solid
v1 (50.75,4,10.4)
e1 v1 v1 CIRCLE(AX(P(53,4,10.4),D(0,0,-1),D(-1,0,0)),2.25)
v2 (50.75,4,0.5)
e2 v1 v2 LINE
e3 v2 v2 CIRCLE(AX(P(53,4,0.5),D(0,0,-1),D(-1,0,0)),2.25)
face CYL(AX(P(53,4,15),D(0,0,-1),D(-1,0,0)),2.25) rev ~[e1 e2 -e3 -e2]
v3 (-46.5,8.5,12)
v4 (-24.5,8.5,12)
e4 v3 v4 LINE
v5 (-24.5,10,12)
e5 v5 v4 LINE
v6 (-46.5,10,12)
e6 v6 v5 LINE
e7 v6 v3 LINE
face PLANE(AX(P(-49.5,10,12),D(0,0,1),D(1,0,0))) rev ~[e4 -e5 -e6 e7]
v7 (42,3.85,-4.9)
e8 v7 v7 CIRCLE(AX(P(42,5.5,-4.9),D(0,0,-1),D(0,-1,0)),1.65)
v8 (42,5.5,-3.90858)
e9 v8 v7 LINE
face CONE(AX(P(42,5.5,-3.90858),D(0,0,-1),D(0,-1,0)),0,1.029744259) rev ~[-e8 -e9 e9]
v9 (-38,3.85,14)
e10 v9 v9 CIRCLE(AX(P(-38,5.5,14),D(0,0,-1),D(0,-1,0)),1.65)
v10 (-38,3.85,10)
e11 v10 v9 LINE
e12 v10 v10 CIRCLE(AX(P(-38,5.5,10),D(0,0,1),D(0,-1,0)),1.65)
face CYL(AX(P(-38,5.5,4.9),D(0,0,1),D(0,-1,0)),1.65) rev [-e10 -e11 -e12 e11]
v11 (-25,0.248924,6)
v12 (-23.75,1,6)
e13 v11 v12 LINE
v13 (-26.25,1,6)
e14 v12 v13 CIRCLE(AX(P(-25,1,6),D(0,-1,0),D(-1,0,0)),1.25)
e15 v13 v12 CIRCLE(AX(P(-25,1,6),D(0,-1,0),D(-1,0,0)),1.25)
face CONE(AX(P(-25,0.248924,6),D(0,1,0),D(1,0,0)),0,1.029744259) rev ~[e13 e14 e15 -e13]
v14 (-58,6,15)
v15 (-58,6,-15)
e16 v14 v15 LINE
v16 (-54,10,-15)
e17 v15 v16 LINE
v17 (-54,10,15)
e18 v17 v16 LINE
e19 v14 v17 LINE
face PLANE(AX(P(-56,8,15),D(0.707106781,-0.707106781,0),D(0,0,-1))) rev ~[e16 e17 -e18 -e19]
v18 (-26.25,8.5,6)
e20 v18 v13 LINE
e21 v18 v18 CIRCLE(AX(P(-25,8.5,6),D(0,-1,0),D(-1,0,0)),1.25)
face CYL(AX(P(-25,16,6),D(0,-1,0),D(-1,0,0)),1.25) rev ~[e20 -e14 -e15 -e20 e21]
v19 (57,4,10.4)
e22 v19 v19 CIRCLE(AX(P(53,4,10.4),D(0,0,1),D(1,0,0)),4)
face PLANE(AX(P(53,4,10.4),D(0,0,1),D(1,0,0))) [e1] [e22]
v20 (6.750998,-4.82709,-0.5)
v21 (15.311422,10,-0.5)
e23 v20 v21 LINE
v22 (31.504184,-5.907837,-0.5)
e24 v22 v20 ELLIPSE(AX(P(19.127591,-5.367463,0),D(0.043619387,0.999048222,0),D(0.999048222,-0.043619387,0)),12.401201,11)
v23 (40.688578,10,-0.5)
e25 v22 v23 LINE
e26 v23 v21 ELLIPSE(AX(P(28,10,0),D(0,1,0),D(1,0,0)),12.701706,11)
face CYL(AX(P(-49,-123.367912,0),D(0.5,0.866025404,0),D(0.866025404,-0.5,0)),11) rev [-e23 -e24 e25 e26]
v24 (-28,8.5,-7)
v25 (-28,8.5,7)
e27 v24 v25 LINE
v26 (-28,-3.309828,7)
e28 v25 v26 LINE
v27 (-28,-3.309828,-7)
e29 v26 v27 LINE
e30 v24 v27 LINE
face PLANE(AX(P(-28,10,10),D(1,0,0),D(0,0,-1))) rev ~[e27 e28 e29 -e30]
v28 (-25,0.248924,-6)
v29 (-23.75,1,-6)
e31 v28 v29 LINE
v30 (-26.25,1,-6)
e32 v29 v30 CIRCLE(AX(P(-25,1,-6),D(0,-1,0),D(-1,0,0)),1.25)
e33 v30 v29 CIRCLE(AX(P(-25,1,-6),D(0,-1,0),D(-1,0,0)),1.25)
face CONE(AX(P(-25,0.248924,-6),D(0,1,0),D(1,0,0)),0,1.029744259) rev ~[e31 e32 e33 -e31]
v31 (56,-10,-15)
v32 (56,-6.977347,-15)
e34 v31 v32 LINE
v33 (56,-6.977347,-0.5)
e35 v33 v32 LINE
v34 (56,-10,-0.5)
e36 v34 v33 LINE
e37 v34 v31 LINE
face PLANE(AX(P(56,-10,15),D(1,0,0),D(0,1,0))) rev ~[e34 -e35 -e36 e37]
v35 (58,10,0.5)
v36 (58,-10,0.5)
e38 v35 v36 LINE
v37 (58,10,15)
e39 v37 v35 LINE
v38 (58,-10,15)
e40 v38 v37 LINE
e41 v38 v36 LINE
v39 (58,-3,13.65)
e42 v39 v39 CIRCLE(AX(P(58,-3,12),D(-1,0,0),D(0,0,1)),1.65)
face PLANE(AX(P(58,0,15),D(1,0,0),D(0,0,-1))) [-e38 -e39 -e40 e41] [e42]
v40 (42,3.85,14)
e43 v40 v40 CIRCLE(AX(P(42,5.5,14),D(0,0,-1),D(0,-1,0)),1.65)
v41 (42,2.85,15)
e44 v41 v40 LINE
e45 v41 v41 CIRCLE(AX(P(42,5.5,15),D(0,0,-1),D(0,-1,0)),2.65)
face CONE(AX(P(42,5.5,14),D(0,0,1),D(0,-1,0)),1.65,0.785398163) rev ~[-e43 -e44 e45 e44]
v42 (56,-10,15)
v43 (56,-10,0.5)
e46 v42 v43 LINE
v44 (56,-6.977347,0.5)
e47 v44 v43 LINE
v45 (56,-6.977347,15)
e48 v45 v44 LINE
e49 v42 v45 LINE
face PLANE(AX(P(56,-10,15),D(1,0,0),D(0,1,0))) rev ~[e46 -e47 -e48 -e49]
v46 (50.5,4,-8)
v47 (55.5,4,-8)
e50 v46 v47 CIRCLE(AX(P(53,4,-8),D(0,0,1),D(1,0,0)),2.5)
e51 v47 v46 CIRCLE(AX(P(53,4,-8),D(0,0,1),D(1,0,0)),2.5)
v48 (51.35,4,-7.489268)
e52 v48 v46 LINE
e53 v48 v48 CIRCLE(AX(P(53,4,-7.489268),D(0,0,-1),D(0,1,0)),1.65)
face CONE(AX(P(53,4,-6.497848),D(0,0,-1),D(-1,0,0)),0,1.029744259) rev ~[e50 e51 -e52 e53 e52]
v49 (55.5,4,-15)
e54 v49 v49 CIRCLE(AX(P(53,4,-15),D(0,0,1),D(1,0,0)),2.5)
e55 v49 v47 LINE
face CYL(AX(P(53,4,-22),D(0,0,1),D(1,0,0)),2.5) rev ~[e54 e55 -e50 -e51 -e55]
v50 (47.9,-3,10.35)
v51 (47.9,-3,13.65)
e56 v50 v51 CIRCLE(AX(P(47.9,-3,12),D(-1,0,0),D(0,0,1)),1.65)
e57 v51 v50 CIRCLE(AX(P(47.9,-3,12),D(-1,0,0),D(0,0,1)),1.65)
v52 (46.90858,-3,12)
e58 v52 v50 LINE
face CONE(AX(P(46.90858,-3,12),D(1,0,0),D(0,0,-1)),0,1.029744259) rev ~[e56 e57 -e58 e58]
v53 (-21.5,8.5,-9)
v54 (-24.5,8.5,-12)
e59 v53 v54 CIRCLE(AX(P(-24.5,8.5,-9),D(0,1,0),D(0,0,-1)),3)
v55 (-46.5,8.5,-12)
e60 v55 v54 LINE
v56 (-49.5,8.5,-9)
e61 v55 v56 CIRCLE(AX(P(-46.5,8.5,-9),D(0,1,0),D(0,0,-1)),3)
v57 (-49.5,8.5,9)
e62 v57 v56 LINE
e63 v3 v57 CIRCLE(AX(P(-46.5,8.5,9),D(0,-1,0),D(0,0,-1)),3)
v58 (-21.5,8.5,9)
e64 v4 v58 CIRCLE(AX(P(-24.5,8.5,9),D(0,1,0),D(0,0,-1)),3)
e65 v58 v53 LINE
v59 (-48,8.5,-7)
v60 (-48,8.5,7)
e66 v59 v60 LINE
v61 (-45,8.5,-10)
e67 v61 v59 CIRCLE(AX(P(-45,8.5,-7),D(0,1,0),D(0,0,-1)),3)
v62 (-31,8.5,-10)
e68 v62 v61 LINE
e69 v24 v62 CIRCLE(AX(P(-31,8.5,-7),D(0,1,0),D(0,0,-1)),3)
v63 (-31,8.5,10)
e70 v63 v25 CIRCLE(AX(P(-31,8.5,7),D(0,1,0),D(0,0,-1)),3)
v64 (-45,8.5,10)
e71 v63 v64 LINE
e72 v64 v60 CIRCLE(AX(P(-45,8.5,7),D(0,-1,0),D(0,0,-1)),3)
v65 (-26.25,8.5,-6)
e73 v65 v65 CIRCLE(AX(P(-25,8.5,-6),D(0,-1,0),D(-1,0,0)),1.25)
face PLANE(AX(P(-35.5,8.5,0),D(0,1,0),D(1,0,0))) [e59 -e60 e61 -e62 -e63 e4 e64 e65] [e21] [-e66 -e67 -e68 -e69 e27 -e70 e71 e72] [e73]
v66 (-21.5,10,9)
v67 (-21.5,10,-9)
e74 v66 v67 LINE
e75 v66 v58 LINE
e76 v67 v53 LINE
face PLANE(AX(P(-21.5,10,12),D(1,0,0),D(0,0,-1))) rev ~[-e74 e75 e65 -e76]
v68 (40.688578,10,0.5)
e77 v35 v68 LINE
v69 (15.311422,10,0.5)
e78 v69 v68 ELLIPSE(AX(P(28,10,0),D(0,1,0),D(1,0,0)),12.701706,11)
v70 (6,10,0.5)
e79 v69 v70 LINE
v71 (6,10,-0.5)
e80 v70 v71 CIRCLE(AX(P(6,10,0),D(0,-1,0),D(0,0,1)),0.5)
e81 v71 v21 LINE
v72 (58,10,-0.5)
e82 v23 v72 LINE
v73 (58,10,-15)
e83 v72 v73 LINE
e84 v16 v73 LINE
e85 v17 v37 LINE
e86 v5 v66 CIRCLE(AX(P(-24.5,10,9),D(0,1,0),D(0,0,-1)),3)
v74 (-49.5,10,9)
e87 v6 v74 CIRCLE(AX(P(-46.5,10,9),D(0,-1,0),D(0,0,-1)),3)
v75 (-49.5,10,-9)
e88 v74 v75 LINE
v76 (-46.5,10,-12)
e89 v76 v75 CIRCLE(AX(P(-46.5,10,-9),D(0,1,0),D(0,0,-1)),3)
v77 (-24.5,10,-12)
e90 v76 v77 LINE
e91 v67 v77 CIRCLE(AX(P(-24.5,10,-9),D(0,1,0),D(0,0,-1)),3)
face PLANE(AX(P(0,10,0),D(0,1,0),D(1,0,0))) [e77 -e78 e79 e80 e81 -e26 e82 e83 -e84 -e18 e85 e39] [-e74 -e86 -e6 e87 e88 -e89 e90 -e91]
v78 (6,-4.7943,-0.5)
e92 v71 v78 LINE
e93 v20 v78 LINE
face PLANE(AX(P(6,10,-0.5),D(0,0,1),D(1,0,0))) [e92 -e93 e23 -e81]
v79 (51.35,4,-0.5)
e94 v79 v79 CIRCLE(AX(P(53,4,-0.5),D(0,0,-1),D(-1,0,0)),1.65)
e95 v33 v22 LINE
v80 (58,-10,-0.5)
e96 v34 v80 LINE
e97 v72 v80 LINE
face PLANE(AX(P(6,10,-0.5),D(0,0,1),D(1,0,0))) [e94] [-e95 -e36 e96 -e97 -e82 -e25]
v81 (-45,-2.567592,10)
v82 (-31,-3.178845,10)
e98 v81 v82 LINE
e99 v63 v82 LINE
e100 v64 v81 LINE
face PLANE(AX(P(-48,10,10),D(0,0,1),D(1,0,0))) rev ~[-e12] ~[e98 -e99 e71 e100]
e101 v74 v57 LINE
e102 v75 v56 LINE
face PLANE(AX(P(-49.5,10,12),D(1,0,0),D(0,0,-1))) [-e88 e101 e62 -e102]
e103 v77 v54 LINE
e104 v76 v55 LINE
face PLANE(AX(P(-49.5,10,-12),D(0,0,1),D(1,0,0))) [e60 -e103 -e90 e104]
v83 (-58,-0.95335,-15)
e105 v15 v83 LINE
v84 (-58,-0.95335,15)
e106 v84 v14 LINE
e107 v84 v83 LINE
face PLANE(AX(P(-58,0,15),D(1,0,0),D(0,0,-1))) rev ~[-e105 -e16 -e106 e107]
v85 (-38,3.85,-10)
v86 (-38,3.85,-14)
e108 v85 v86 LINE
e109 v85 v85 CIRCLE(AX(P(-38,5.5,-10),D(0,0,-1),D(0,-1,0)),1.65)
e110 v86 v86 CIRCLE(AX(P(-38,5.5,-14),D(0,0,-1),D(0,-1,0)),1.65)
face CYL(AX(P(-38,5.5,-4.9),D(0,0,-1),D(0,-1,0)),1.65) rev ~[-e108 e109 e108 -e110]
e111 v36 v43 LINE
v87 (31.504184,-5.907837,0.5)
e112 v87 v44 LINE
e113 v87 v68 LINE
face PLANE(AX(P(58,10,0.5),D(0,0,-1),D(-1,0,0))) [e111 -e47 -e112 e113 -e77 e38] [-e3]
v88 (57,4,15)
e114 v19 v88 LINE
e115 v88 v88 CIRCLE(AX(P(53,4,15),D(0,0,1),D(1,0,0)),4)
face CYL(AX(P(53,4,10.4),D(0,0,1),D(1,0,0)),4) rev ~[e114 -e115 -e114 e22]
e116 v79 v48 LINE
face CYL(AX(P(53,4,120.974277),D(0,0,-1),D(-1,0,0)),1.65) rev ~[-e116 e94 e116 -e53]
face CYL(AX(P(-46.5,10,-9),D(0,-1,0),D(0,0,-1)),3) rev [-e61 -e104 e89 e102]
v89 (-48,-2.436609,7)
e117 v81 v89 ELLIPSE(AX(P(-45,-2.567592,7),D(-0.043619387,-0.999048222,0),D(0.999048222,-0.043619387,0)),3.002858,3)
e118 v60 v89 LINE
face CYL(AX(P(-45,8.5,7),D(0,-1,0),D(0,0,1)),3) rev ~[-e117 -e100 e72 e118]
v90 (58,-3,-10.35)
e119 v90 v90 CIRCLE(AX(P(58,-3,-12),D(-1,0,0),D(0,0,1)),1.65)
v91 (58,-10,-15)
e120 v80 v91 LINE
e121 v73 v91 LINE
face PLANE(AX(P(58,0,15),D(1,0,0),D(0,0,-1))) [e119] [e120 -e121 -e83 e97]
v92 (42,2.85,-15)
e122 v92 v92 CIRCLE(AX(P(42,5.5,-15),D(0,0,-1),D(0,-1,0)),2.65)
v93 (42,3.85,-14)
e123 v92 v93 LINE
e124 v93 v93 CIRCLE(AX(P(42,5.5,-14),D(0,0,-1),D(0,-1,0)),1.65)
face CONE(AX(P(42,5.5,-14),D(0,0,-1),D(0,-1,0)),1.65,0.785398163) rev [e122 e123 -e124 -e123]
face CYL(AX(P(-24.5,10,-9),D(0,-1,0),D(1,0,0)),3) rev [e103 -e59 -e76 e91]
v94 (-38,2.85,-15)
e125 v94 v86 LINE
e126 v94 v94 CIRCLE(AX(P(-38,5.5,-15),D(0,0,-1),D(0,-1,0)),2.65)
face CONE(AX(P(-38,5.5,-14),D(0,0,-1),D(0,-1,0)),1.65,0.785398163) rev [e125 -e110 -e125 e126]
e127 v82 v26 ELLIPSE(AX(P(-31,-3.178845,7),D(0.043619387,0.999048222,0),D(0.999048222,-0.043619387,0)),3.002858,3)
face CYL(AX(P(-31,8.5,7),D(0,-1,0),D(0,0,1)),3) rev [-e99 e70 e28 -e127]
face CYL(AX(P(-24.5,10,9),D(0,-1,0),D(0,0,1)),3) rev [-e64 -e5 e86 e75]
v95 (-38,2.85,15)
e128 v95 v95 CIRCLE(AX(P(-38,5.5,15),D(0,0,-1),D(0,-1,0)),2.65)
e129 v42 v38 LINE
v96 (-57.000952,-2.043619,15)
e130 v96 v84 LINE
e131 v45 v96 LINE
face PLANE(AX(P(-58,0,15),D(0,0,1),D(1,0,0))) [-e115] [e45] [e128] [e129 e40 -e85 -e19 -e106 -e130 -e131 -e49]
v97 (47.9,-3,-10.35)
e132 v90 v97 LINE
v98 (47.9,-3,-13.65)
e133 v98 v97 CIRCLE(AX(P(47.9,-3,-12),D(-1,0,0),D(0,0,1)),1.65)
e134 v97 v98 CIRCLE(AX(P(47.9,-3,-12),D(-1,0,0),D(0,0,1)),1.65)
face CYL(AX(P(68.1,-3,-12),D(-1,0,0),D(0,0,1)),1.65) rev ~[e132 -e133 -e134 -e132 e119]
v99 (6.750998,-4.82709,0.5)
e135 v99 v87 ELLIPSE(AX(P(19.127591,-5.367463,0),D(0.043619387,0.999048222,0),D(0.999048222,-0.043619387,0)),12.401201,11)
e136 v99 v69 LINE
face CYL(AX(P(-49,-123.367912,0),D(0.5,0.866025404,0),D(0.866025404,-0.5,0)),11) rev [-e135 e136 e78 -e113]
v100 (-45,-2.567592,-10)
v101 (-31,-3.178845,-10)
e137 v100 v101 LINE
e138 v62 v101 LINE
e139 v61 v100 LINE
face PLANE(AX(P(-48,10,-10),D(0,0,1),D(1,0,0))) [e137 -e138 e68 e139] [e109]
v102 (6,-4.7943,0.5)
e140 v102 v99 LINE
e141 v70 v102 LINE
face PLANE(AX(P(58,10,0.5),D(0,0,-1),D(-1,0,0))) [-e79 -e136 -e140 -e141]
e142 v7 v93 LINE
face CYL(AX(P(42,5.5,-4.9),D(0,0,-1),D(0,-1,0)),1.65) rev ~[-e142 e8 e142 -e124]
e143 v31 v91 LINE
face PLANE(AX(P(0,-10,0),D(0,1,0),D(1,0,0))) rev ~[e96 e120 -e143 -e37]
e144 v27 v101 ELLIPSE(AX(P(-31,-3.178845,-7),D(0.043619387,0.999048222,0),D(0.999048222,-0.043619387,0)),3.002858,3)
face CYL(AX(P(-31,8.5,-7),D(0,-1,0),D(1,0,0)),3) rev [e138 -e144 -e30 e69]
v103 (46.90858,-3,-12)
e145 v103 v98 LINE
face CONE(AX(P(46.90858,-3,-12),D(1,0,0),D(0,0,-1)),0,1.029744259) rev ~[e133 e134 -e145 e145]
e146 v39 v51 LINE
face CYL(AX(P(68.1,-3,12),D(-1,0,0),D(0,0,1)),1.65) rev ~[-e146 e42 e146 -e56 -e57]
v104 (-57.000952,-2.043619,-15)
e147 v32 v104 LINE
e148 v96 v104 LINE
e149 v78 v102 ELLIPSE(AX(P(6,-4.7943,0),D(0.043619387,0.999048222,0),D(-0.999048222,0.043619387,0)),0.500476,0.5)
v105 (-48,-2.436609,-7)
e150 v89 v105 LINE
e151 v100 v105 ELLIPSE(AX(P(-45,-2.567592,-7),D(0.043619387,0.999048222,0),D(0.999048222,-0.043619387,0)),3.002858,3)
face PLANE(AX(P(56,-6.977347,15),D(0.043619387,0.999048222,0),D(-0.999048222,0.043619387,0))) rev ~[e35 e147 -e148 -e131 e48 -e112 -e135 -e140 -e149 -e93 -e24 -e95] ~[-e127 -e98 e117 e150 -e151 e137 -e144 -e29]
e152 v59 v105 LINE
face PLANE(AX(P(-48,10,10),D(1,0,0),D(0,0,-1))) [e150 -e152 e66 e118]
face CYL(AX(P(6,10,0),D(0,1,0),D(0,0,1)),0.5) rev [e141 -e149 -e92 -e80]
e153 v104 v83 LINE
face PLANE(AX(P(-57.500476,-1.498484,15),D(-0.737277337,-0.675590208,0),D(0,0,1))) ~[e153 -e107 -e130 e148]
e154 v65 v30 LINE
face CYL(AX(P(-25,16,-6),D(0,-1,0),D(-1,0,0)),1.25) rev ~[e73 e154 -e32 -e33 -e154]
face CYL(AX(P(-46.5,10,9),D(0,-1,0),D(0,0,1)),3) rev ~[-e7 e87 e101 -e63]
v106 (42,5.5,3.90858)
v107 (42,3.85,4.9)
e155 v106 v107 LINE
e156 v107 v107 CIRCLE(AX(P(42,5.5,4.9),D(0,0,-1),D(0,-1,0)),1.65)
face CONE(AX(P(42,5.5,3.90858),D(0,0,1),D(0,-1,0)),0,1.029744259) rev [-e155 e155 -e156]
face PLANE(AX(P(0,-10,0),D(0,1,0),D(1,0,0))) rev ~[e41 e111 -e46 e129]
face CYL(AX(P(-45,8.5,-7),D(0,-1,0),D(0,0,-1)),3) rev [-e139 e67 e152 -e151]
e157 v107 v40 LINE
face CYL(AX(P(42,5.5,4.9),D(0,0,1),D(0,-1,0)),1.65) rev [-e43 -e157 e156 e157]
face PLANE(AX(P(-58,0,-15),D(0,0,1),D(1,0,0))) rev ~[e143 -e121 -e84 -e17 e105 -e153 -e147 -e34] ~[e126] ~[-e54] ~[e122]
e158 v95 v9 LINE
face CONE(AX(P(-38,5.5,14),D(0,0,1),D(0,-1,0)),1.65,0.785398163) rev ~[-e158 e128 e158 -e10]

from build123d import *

# Parameters (mm, degrees)
SKETCH1_W                                            = 116
SKETCH1_H                                            = 30
BOSS_EXTRUDE1_DEPTH                                  = 10
CUT_EXTRUDE2_DEPTH                                   = 64.158530699
HOLE_SIZE_PER_SOCKET_HEAD_CAP_SCREW_TYPE_D           = 4.5
HOLE_SIZE_PER_SOCKET_HEAD_CAP_SCREW_TYPE_DEPTH       = 14.5
HOLE_SIZE_PER_SOCKET_HEAD_CAP_SCREW_TYPE_CBORE_D     = 8
HOLE_SIZE_PER_SOCKET_HEAD_CAP_SCREW_TYPE_CBORE_DEPTH = 4.6
M4_TAPPED_HOLE1_D                                    = 3.3
F_5_0_5_DIAMETER_HOLE1_D                             = 5
F_5_0_5_DIAMETER_HOLE1_DEPTH                         = 7
F_5_0_5_DIAMETER_HOLE1_TIP                           = 1.502151548
M4_TAPPED_HOLE2_AT_2_COUNT                           = 2
M4_TAPPED_HOLE2_AT_2_PITCH                           = 80
CHAMFER1_SIZE                                        = 4
M4_TAPPED_HOLE3_D                                    = 3.3
M4_TAPPED_HOLE3_DEPTH                                = 10.1
M4_TAPPED_HOLE3_TIP                                  = 0.991420021
CUT_EXTRUDE3_DEPTH                                   = 67.060578275
SKETCH18_W                                           = 20
SKETCH18_H                                           = 20
CUT_EXTRUDE4_DEPTH                                   = 64.158530699
SKETCH19_W                                           = 28
SKETCH19_H                                           = 24
CUT_EXTRUDE5_DEPTH                                   = 1.5
FILLET1_R                                            = 3
M3_TAPPED_HOLE1_D                                    = 2.5
M3_TAPPED_HOLE1_DEPTH                                = 7.5
M3_TAPPED_HOLE1_TIP                                  = 0.751075774
CHAMFER2_SIZE                                        = 1
CHAMFER2_SIZE2                                       = 1.04665043
CHAMFER3_SIZE                                        = 1


with BuildPart() as part:
    # Sketch1 → Boss-Extrude1 (new, symmetric)
    with BuildSketch(Plane(origin=(0, 0, 0), x_dir=(1, 0, 0), z_dir=(0, 1, 0))):
        Rectangle(SKETCH1_W, SKETCH1_H)
    extrude(amount=BOSS_EXTRUDE1_DEPTH, both=True)

    # Sketch3 → Cut-Revolve1 (revolve, cut)
    with BuildSketch(Plane.XY):
        Polygon((-39.473720558, -128.867912183), (58.526279442, 40.873066959), (49, 46.373066959), (-49, -123.367912183), align=None)
    revolve(axis=Axis((28, 10, 0), (-0.5000000000000041, -0.8660254037844363, 0)), mode=Mode.SUBTRACT)

    # Sketch4 → Cut-Extrude2 (cut, through all)
    with BuildSketch(Plane(origin=(0, 10, 0), x_dir=(1, 0, 0), z_dir=(0, 1, 0))):
        with BuildLine():
            Line((6, 0.5), (58, 0.5))
            Line((58, 0.5), (58, -0.5))
            Line((58, -0.5), (6, -0.5))
            ThreePointArc((6, -0.5), (5.5, 0), (6, 0.5))
        make_face()
    extrude(amount=-CUT_EXTRUDE2_DEPTH, mode=Mode.SUBTRACT)

    # Hole size per socket head cap screw type1
    with Locations(Plane.XY.offset(15)):
        with Locations((53, 4)):
            CounterBoreHole(HOLE_SIZE_PER_SOCKET_HEAD_CAP_SCREW_TYPE_D / 2, HOLE_SIZE_PER_SOCKET_HEAD_CAP_SCREW_TYPE_CBORE_D / 2, HOLE_SIZE_PER_SOCKET_HEAD_CAP_SCREW_TYPE_CBORE_DEPTH, depth=HOLE_SIZE_PER_SOCKET_HEAD_CAP_SCREW_TYPE_DEPTH)

    # M4 Tapped Hole1 (through all)
    with Locations(Plane.XY.offset(-0.5)):
        with Locations((53, 4)):
            Hole(M4_TAPPED_HOLE1_D / 2)

    # Ø5.0 (5) Diameter Hole1
    with Locations(Plane(origin=(0, 0, -15), x_dir=(-1, 0, 0), z_dir=(0, 0, -1))):
        with Locations((-53, 4)):
            Hole(F_5_0_5_DIAMETER_HOLE1_D / 2, depth=F_5_0_5_DIAMETER_HOLE1_DEPTH)
            with Locations((0, 0, -(F_5_0_5_DIAMETER_HOLE1_DEPTH + F_5_0_5_DIAMETER_HOLE1_TIP / 2))):  # 118° drill point
                Cone(0, F_5_0_5_DIAMETER_HOLE1_D / 2, F_5_0_5_DIAMETER_HOLE1_TIP, mode=Mode.SUBTRACT)

    # Sketch11 → M4 Tapped Hole2 (revolve, cut)
    with BuildSketch(Plane(origin=(-38, 5.5, 15), x_dir=(0, -1, 0), z_dir=(1, 0, 0))):
        Polygon((0, 0), (0, 11.091420021), (1.65, 10.1), (1.65, 0), align=None)
    m4_tapped_hole2 = revolve(axis=Axis((-38, 5.5, 21.35), (0, 0, -1)), mode=Mode.SUBTRACT)

    # M4 Tapped Hole2 at 2: M4 Tapped Hole2 ×2
    with Locations(*[(i * M4_TAPPED_HOLE2_AT_2_PITCH, 0, 0) for i in range(1, M4_TAPPED_HOLE2_AT_2_COUNT)]):
        add(m4_tapped_hole2, mode=Mode.SUBTRACT)

    # Mirror1: M4 Tapped Hole2 across plane
    add(m4_tapped_hole2.mirror(Plane.XY), mode=Mode.SUBTRACT)

    # Mirror1 copy 1 sketch → Mirror1 copy 1 (revolve, cut)
    with BuildSketch(Plane(origin=(42, 5.5, -15), x_dir=(0, -1, 0), z_dir=(1, 0, 0))):
        Polygon((0, 0), (0, -11.091420021), (1.65, -10.1), (1.65, 0), align=None)
    revolve(axis=Axis((42, 5.5, -21.35), (0, 0, -1)), mode=Mode.SUBTRACT)

    # Chamfer1
    chamfer1_edges = [part.edges().sort_by_distance(p)[0] for p in [
        (-58, 10, 0),
    ]]
    chamfer(chamfer1_edges, length=CHAMFER1_SIZE)

    # M4 Tapped Hole3
    with Locations(Plane(origin=(58, 0, 0), x_dir=(0, 0, -1), z_dir=(1, 0, 0))):
        with Locations((-12, -3), (12, -3)):
            Hole(M4_TAPPED_HOLE3_D / 2, depth=M4_TAPPED_HOLE3_DEPTH)
            with Locations((0, 0, -(M4_TAPPED_HOLE3_DEPTH + M4_TAPPED_HOLE3_TIP / 2))):  # 118° drill point
                Cone(0, M4_TAPPED_HOLE3_D / 2, M4_TAPPED_HOLE3_TIP, mode=Mode.SUBTRACT)

    # Sketch17 → Cut-Extrude3 (cut, through all)
    with BuildSketch(Plane.XY.offset(15)):
        Polygon((-58, -10), (56, -10), (56, -6.977347492), (-58, -2), align=None)
    extrude(amount=-CUT_EXTRUDE3_DEPTH, mode=Mode.SUBTRACT)

    # Sketch18 → Cut-Extrude4 (cut, through all)
    with BuildSketch(Plane(origin=(0, 10, 0), x_dir=(1, 0, 0), z_dir=(0, 1, 0))):
        with Locations((-38, 0)):
            Rectangle(SKETCH18_W, SKETCH18_H)
    extrude(amount=-CUT_EXTRUDE4_DEPTH, mode=Mode.SUBTRACT)

    # Sketch19 → Cut-Extrude5 (cut)
    with BuildSketch(Plane(origin=(0, 10, 0), x_dir=(1, 0, 0), z_dir=(0, 1, 0))):
        with Locations((-35.5, 0)):
            Rectangle(SKETCH19_W, SKETCH19_H)
    extrude(amount=-CUT_EXTRUDE5_DEPTH, mode=Mode.SUBTRACT)

    # Fillet1
    fillet1_edges = [part.edges().sort_by_distance(p)[0] for p in [
        (-48, 3.031695285, 10),
        (-48, 3.031695285, -10),
        (-28, 2.595085856, -10),
        (-28, 2.595085856, 10),
        (-49.5, 9.25, 12),
        (-49.5, 9.25, -12),
        (-21.5, 9.25, -12),
        (-21.5, 9.25, 12),
    ]]
    fillet(fillet1_edges, radius=FILLET1_R)

    # M3 Tapped Hole1
    with Locations(Plane(origin=(0, 8.5, 0), x_dir=(1, 0, 0), z_dir=(0, 1, 0))):
        with Locations((-25, 6), (-25, -6)):
            Hole(M3_TAPPED_HOLE1_D / 2, depth=M3_TAPPED_HOLE1_DEPTH)
            with Locations((0, 0, -(M3_TAPPED_HOLE1_DEPTH + M3_TAPPED_HOLE1_TIP / 2))):  # 118° drill point
                Cone(0, M3_TAPPED_HOLE1_D / 2, M3_TAPPED_HOLE1_TIP, mode=Mode.SUBTRACT)

    # Chamfer2
    chamfer2_edges = [part.edges().sort_by_distance(p)[0] for p in [
        (-58, -2, 0),
    ]]
    chamfer2_side = [part.faces().sort_by_distance(p)[0] for p in [
        (0.861914044, -4.569966669, 0),
    ]]
    chamfer(chamfer2_edges, length=CHAMFER2_SIZE, length2=CHAMFER2_SIZE2, reference=chamfer2_side[0])

    # Chamfer3
    chamfer3_edges = [part.edges().sort_by_distance(p)[0] for p in [
        (42, 7.15, 15),
        (-38, 7.15, 15),
        (42, 7.15, -15),
        (-38, 7.15, -15),
    ]]
    chamfer(chamfer3_edges, length=CHAMFER3_SIZE)


solid = part.part
